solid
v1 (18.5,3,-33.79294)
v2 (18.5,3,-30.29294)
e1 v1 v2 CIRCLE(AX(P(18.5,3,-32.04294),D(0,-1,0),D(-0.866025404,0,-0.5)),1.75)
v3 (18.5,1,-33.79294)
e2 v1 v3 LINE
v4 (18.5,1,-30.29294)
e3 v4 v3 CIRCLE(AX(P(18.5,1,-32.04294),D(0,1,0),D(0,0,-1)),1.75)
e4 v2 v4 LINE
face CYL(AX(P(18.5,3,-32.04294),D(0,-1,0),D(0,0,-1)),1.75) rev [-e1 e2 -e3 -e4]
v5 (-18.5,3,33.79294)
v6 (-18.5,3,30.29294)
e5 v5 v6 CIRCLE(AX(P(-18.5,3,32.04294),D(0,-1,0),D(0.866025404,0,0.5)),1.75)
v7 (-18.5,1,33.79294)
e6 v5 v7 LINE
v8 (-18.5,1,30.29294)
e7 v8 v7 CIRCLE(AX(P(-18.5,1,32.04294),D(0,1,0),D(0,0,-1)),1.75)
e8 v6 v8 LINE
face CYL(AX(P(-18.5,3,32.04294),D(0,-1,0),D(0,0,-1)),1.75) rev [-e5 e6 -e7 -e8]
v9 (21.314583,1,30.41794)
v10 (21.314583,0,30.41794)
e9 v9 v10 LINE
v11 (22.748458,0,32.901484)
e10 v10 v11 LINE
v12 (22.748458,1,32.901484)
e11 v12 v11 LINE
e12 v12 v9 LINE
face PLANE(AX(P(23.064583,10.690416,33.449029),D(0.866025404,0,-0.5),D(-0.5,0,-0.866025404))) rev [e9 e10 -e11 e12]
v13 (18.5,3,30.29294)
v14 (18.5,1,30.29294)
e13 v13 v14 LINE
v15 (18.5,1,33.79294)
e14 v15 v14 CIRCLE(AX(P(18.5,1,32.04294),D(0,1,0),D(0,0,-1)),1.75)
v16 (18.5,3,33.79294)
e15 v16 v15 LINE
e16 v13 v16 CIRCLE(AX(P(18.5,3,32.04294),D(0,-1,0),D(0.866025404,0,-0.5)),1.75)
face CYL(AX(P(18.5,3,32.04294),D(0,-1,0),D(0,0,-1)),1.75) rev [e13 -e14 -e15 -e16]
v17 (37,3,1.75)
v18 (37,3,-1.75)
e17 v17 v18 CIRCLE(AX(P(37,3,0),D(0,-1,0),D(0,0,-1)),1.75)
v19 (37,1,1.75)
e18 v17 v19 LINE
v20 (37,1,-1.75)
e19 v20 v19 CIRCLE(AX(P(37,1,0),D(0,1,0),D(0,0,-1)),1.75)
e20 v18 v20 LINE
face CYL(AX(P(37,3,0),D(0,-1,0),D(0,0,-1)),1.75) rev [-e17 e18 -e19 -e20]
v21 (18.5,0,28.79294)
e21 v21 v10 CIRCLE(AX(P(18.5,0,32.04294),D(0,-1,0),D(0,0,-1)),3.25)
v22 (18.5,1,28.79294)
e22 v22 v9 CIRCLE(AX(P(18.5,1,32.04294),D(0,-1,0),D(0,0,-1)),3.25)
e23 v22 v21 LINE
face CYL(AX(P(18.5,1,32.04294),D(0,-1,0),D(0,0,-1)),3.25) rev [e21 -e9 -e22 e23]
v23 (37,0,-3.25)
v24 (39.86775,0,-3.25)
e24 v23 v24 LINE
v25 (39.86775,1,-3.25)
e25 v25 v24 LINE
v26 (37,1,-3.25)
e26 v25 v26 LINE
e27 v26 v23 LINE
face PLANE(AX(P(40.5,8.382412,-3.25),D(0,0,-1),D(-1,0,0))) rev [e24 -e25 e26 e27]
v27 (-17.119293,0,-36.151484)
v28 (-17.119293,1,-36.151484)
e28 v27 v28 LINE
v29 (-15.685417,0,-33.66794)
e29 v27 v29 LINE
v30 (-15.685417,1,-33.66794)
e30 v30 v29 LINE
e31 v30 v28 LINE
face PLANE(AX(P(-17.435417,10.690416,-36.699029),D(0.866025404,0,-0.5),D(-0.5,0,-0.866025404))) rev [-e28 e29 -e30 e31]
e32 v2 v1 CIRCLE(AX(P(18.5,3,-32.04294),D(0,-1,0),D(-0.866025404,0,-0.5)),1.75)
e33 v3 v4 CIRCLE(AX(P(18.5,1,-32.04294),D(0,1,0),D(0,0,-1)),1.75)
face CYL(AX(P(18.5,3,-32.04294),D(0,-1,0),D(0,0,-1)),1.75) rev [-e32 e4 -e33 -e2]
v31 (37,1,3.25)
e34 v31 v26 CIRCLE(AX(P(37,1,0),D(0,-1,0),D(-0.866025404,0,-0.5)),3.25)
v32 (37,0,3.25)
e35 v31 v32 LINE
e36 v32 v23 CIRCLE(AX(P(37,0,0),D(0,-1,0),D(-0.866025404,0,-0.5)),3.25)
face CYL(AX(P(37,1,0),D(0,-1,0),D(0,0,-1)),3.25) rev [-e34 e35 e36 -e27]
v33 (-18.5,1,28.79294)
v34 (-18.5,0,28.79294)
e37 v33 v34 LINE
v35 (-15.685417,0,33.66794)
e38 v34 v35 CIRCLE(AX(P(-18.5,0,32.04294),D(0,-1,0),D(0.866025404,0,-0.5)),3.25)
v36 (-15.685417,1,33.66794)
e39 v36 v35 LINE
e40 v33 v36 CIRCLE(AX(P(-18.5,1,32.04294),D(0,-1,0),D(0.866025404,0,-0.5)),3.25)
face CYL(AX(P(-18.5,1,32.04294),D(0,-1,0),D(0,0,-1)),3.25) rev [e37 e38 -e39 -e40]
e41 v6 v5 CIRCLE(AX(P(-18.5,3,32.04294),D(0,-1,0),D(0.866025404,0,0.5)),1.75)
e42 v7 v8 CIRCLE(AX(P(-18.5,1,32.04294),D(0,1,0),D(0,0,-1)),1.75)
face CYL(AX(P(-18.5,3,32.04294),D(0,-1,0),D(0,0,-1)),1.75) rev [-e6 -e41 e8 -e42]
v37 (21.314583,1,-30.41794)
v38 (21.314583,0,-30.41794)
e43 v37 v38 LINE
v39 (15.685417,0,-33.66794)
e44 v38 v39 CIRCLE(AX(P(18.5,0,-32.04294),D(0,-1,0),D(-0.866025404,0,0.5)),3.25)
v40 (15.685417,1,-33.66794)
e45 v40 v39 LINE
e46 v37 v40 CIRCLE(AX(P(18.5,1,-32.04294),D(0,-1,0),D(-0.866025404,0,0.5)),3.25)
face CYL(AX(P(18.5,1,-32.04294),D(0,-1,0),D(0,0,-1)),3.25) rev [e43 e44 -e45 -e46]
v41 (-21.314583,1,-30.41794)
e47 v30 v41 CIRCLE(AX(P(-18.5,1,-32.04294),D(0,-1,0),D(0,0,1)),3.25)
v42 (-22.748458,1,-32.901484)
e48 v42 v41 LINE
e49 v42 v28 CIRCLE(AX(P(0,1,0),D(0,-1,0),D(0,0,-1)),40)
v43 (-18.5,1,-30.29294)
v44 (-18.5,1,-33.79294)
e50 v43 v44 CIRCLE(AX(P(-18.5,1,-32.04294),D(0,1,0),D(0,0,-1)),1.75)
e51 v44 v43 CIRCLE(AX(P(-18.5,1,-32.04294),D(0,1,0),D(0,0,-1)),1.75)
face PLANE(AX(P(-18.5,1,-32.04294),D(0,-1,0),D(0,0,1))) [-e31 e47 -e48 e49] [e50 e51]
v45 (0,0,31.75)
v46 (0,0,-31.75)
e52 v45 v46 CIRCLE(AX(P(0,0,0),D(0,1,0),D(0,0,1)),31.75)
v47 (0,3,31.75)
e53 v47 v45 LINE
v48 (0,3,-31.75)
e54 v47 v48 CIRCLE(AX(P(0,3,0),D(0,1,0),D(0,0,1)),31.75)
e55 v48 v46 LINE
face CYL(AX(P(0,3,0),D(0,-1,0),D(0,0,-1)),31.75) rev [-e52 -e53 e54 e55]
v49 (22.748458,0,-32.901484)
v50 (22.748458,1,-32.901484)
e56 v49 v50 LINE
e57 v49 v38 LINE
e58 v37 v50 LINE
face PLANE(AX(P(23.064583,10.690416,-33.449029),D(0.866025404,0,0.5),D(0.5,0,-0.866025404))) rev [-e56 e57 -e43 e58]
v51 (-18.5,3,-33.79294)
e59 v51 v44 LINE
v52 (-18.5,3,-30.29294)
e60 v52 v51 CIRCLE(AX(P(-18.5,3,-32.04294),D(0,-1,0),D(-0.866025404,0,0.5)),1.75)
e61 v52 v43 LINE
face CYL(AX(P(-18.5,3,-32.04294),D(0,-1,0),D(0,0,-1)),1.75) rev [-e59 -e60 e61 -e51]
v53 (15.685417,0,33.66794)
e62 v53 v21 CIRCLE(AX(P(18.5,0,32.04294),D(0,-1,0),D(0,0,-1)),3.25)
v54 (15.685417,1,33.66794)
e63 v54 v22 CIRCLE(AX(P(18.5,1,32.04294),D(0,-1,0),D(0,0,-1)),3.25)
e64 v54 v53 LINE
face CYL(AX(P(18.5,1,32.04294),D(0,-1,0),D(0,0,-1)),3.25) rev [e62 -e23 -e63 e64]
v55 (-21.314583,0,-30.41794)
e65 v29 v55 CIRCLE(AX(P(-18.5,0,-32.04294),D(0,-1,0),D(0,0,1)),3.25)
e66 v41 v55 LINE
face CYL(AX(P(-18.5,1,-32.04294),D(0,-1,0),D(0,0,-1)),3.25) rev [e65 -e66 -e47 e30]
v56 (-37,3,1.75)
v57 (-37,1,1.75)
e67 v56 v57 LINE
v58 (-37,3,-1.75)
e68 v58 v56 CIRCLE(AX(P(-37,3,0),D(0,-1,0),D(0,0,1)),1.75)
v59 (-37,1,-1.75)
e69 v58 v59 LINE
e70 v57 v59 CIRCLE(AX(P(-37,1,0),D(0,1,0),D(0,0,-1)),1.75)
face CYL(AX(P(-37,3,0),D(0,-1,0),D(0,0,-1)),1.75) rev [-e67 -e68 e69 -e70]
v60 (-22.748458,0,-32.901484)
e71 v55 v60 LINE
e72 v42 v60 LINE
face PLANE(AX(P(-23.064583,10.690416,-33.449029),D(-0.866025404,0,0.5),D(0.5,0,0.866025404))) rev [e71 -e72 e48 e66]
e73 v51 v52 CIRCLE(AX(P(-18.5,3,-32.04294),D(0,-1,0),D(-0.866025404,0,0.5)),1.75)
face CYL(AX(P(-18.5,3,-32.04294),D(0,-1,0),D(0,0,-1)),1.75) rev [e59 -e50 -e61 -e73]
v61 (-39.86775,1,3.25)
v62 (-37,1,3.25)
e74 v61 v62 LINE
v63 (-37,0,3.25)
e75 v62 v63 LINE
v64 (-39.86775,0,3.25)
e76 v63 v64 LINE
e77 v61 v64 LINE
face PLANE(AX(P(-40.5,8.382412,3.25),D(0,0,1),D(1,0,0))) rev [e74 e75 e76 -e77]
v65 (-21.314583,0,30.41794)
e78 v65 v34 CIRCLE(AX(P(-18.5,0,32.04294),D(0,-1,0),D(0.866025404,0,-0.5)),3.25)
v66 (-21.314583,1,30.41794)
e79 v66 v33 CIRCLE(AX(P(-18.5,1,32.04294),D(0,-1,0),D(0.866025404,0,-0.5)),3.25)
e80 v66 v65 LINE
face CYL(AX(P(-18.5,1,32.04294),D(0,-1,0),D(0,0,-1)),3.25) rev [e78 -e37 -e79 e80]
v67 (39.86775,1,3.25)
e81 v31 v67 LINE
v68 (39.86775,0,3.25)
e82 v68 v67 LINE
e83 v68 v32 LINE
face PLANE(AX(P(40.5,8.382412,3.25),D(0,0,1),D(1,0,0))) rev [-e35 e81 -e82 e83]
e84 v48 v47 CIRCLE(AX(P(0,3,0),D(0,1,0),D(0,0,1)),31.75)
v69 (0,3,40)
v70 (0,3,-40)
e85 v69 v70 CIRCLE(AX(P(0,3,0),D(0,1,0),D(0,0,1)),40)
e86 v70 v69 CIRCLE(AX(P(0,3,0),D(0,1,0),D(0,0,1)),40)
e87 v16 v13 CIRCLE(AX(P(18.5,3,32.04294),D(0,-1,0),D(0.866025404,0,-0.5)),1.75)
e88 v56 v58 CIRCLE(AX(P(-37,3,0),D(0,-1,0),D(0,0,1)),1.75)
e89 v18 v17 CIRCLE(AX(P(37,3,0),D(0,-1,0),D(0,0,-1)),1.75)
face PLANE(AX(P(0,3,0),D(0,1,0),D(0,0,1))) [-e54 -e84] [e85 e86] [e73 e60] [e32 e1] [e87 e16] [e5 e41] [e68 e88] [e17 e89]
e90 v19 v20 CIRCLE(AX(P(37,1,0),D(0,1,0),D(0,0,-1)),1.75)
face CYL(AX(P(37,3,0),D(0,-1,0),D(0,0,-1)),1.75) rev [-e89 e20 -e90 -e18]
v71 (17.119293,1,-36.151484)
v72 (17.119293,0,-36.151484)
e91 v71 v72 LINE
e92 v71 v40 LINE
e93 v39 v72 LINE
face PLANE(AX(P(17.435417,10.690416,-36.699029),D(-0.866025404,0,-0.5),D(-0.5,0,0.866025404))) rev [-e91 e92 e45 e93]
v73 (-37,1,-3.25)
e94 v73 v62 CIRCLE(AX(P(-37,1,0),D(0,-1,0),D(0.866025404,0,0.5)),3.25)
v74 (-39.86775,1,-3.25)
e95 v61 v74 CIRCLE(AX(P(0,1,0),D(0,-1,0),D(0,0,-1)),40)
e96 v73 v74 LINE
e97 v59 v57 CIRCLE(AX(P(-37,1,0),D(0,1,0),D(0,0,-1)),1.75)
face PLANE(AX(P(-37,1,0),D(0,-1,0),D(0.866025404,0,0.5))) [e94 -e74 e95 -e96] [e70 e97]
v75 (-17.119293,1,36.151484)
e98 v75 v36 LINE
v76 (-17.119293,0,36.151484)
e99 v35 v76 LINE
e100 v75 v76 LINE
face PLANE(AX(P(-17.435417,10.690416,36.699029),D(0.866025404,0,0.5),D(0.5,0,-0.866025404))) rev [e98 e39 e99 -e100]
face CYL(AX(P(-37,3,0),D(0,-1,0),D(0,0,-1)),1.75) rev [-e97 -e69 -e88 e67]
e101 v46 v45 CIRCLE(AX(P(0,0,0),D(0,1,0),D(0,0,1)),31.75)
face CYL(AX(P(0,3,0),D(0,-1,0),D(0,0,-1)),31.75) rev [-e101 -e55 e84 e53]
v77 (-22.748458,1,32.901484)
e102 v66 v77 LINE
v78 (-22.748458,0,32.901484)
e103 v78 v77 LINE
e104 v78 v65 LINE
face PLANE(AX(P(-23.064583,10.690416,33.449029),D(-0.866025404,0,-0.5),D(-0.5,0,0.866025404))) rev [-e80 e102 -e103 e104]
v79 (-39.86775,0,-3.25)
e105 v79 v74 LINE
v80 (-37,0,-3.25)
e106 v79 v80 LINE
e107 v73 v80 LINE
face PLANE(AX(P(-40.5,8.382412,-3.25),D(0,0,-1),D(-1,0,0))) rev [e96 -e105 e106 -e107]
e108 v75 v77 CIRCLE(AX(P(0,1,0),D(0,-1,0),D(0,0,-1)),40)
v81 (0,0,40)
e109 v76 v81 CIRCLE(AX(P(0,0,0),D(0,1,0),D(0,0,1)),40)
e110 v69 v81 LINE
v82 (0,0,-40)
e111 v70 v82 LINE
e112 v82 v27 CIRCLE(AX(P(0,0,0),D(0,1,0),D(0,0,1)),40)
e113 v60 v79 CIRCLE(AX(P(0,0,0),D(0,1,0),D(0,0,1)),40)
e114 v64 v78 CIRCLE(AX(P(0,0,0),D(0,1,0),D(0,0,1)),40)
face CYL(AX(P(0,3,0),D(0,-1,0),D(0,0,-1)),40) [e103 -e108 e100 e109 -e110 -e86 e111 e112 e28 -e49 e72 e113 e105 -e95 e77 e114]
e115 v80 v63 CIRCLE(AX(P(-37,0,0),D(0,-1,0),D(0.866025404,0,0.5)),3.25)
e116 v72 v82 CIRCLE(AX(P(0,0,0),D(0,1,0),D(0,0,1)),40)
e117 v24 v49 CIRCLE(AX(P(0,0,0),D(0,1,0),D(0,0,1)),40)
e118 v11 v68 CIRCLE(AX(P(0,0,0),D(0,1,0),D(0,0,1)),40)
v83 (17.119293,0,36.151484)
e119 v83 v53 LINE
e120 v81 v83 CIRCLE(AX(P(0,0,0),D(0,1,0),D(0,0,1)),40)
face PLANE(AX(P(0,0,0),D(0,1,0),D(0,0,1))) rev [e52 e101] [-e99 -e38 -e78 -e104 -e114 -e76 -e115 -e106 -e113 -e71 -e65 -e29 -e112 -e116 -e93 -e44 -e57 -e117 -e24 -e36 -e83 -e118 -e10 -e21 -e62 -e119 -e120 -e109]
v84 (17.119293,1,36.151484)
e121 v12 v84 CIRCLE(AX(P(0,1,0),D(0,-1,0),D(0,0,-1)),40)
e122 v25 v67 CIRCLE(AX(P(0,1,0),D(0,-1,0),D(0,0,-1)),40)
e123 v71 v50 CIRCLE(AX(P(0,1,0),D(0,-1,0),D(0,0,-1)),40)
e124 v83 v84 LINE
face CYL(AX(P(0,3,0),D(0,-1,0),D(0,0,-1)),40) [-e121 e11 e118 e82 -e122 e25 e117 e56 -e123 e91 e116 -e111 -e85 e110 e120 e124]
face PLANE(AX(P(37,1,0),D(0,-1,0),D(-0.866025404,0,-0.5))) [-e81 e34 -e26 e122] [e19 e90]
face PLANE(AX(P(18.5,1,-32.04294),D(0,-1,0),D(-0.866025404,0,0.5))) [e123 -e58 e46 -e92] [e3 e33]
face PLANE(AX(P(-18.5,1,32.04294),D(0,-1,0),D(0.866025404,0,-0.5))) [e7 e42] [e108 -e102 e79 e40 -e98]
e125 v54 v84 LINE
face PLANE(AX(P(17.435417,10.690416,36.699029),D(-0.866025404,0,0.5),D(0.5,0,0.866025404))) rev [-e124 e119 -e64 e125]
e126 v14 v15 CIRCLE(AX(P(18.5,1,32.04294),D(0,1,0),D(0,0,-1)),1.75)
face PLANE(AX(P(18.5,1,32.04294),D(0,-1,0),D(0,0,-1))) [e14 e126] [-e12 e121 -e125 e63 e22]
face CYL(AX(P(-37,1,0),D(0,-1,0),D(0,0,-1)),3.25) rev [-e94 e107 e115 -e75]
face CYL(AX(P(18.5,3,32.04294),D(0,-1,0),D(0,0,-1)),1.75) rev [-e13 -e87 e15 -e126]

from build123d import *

# Parameters (mm, degrees)
SKETCH1_R           = 40
SKETCH1_R_2         = 31.75
BOSS_EXTRUDE1_DEPTH = 3
SKETCH3_R           = 1.75
CUT_EXTRUDE2_DEPTH  = 57.648036153
CIRPATTERN1_COUNT   = 6
SKETCH5_R           = 3.25
CUT_EXTRUDE4_DEPTH  = 1
CIRPATTERN2_COUNT   = 6
SKETCH6_W           = 3.5
SKETCH6_H           = 6.5
CUT_EXTRUDE5_DEPTH  = 1
CIRPATTERN3_COUNT   = 6


with BuildPart() as part:
    # Sketch1 → Boss-Extrude1 (new body)
    with BuildSketch(Plane(origin=(0, 0, 0), x_dir=(1, 0, 0), z_dir=(0, 1, 0))):
        with Locations(Location((0, 0, 0), (0, 0, 270))):
            Circle(SKETCH1_R)
        with Locations(Location((0, 0, 0), (0, 0, 270))):
            Circle(SKETCH1_R_2, mode=Mode.SUBTRACT)
    extrude(amount=BOSS_EXTRUDE1_DEPTH)

    # Sketch3 → Cut-Extrude2 (cut, through all)
    with BuildSketch(Plane.XZ):
        with Locations(Location((37, 0, 0), (0, 0, 270))):
            Circle(SKETCH3_R)
    cut_extrude2 = extrude(amount=-CUT_EXTRUDE2_DEPTH, mode=Mode.SUBTRACT)

    # CirPattern1: Cut-Extrude2 ×6 about axis
    cirpattern1_axis = Axis((0, 0, 0), (0, 1, 0))
    for i in range(1, CIRPATTERN1_COUNT):
        add(cut_extrude2.rotate(cirpattern1_axis, i * 360 / CIRPATTERN1_COUNT), mode=Mode.SUBTRACT)

    # Sketch5 → Cut-Extrude4 (cut)
    with BuildSketch(Plane.XZ):
        with Locations((18.5, 32.04293994)):
            Circle(SKETCH5_R)
    cut_extrude4 = extrude(amount=-CUT_EXTRUDE4_DEPTH, mode=Mode.SUBTRACT)

    # CirPattern2: Cut-Extrude4 ×6 about axis
    cirpattern2_axis = Axis((0, 0, 0), (0, 1, 0))
    for i in range(1, CIRPATTERN2_COUNT):
        add(cut_extrude4.rotate(cirpattern2_axis, i * 360 / CIRPATTERN2_COUNT), mode=Mode.SUBTRACT)

    # Sketch6 → Cut-Extrude5 (cut)
    with BuildSketch(Plane.XZ):
        with Locations((38.75, 0)):
            Rectangle(SKETCH6_W, SKETCH6_H)
    cut_extrude5 = extrude(amount=-CUT_EXTRUDE5_DEPTH, mode=Mode.SUBTRACT)

    # CirPattern3: Cut-Extrude5 ×6 about axis
    cirpattern3_axis = Axis((0, 0, 0), (0, 1, 0))
    for i in range(1, CIRPATTERN3_COUNT):
        add(cut_extrude5.rotate(cirpattern3_axis, i * 360 / CIRPATTERN3_COUNT), mode=Mode.SUBTRACT)


solid = part.part
